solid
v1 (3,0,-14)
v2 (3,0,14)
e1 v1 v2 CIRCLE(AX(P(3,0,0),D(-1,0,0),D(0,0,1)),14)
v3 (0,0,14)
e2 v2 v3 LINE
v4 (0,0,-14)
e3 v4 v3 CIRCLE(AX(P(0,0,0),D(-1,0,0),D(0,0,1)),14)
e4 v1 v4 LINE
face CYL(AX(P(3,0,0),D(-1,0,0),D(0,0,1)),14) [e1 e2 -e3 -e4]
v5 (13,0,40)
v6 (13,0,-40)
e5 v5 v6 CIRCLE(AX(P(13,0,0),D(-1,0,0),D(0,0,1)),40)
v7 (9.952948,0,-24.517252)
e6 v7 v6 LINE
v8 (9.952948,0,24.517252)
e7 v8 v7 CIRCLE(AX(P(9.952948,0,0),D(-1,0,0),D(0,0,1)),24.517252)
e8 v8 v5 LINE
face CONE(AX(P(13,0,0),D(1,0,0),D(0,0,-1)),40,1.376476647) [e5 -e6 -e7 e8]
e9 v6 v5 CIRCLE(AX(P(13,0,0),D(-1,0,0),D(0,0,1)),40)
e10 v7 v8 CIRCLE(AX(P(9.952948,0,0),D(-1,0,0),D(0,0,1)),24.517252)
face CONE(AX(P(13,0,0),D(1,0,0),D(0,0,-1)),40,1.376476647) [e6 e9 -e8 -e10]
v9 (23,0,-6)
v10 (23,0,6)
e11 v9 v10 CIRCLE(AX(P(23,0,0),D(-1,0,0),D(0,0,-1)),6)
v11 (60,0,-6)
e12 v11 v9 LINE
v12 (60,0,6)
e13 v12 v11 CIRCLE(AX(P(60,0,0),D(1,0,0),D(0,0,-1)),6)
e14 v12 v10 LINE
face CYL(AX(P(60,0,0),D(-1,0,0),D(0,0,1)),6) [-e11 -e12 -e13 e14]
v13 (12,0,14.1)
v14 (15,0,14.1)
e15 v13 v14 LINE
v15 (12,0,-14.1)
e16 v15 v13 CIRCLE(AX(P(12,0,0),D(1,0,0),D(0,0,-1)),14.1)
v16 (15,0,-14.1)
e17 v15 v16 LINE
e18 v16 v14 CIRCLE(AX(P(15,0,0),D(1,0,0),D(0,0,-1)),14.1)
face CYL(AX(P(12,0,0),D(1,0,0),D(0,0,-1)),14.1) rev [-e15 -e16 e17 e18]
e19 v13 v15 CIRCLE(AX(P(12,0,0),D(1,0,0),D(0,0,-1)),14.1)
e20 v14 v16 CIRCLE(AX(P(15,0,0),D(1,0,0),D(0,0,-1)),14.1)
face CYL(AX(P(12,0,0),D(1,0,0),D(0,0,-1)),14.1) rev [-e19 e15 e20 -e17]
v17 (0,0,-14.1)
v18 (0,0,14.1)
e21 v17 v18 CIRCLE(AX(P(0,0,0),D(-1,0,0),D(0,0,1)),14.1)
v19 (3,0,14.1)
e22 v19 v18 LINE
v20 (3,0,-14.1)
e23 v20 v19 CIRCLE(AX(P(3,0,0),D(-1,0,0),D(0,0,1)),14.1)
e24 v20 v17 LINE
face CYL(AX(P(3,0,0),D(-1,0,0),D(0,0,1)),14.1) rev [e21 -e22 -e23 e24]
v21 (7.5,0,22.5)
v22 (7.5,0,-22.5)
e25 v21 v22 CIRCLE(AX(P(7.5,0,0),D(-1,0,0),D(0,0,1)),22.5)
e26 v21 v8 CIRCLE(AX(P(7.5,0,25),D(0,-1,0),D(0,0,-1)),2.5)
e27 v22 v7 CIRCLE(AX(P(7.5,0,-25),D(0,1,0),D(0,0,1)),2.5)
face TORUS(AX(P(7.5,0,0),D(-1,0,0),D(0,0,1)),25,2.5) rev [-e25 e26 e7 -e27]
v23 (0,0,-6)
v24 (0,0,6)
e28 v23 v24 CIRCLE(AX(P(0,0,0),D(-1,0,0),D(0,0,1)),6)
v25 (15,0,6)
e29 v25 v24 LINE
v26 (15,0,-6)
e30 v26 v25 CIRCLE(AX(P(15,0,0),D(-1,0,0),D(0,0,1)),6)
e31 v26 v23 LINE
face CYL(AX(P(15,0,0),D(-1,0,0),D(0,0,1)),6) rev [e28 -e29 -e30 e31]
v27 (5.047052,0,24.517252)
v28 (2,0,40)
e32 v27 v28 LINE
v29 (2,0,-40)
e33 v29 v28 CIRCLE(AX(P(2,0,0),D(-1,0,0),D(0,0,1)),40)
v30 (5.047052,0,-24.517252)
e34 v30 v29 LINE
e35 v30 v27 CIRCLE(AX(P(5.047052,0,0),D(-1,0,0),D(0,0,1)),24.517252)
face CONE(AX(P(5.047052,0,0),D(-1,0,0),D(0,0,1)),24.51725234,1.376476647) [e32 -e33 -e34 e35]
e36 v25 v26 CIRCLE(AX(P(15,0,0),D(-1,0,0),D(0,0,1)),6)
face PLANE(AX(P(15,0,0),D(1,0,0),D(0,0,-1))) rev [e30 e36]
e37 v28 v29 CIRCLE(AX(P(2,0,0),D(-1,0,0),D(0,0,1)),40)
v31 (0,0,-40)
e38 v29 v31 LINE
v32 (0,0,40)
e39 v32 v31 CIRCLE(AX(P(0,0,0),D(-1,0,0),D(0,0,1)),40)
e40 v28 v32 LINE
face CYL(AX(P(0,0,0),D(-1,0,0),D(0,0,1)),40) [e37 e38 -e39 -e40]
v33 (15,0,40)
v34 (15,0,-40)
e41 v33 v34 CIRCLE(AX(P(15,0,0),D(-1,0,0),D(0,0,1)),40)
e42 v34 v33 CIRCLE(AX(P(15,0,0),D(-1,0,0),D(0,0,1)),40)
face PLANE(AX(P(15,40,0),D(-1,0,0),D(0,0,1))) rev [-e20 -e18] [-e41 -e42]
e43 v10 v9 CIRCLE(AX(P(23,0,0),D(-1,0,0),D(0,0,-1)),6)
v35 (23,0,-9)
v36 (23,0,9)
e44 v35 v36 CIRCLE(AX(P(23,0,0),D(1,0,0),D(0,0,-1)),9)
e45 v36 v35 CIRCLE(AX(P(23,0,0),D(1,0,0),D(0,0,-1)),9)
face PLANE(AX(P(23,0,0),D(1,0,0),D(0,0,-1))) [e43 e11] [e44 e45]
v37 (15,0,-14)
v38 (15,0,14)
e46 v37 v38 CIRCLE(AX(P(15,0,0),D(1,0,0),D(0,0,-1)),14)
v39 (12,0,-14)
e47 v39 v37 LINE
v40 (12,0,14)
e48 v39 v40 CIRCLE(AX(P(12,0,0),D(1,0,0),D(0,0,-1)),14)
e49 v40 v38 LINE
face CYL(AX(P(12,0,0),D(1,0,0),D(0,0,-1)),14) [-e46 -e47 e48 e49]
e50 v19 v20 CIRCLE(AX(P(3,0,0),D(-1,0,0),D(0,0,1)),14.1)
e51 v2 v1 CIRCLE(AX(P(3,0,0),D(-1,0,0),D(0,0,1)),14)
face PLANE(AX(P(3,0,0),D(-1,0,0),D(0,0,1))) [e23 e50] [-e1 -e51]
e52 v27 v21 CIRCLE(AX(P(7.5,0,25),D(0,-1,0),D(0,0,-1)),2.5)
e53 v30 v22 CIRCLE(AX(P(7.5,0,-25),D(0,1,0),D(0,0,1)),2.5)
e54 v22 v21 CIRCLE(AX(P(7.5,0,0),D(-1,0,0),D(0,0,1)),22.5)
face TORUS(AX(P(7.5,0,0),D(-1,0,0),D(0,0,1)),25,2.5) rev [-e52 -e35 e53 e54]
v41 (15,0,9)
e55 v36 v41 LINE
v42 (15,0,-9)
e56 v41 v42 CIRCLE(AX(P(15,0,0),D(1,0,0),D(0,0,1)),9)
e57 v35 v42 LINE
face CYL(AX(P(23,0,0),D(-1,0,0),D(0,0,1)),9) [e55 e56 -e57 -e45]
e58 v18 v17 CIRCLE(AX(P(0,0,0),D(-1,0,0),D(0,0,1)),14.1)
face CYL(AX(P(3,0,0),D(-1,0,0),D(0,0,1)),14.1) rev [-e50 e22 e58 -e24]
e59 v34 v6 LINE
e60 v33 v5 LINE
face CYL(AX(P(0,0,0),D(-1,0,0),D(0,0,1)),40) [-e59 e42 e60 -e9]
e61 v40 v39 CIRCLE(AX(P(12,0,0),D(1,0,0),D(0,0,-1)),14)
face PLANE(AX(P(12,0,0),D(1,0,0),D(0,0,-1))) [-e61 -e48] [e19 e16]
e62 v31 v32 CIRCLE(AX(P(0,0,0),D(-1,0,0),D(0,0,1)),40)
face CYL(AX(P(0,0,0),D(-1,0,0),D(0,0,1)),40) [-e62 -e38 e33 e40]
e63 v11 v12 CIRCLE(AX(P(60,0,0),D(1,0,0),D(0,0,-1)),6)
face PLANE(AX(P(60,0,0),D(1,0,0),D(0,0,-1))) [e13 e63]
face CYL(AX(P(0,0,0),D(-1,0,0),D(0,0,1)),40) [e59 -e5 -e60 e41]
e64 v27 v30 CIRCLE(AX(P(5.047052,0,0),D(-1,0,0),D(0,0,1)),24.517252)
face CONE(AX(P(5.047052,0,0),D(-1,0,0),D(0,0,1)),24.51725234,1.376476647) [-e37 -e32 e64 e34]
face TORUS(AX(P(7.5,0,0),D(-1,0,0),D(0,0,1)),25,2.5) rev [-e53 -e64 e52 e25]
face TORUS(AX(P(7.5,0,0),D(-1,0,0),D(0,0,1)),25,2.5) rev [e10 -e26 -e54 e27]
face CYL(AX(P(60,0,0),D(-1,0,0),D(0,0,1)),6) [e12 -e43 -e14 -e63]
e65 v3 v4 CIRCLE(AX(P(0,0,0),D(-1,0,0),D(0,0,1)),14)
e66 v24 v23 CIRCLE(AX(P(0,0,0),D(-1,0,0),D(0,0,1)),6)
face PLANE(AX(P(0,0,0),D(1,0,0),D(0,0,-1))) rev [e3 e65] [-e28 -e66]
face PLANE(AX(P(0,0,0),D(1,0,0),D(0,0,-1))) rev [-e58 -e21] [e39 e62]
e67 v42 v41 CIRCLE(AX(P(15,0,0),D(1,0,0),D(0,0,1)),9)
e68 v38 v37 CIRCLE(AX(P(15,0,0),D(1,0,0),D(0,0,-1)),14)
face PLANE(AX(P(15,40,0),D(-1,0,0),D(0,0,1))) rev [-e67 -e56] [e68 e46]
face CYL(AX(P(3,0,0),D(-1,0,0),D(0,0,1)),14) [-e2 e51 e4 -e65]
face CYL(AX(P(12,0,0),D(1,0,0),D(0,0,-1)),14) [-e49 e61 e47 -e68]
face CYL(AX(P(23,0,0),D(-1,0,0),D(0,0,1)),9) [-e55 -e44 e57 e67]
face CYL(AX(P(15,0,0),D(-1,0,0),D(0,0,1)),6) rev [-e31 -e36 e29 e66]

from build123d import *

# Parameters (mm, degrees)
SKETCH2_R           = 6
CUT_EXTRUDE1_DEPTH  = 59.523499554
SKETCH3_R           = 14.1
SKETCH3_R_2         = 14
CUT_EXTRUDE2_DEPTH  = 3
CUT_EXTRUDE3_START  = -3
SKETCH4_R           = 14.1
SKETCH4_R_2         = 14
CUT_EXTRUDE3_DEPTH  = 3
SKETCH5_R           = 6
BOSS_EXTRUDE1_DEPTH = 45
SKETCH6_R           = 9
BOSS_EXTRUDE2_DEPTH = 8


with BuildPart() as part:
    # Sketch1 → Revolve1 (revolve)
    with BuildSketch(Plane.XY, mode=Mode.PRIVATE) as revolve1_sk:
        with BuildLine():
            Line((0, 0), (0, 40))
            Line((0, 40), (2, 40))
            Line((2, 40), (5.047051836, 24.51725234))
            ThreePointArc((5.047051836, 24.51725234), (7.5, 22.5), (9.952948164, 24.51725234))
            Line((9.952948164, 24.51725234), (13, 40))
            Line((13, 40), (15, 40))
            Line((15, 40), (15, 0))
            Line((15, 0), (0, 0))
        make_face()
    revolve(revolve1_sk.sketch.rotate(Axis((0, 0, 0), (1, 0, 0)), 90), axis=Axis((0, 0, 0), (1, 0, 0)))

    # Sketch2 → Cut-Extrude1 (cut, through all)
    with BuildSketch(Plane.ZY):
        Circle(SKETCH2_R)
    extrude(amount=-CUT_EXTRUDE1_DEPTH, mode=Mode.SUBTRACT)

    # Sketch3 → Cut-Extrude2 (cut)
    with BuildSketch(Plane.ZY):
        Circle(SKETCH3_R)
        Circle(SKETCH3_R_2, mode=Mode.SUBTRACT)
    extrude(amount=-CUT_EXTRUDE2_DEPTH, mode=Mode.SUBTRACT)

    # Sketch4 → Cut-Extrude3 (cut)
    with BuildSketch(Plane(origin=(15, 0, 0), x_dir=(0, 0, -1), z_dir=(1, 0, 0)).offset(CUT_EXTRUDE3_START)):
        with Locations(Location((0, 0, 0), (0, 0, 180))):
            Circle(SKETCH4_R)
        with Locations(Location((0, 0, 0), (0, 0, 180))):
            Circle(SKETCH4_R_2, mode=Mode.SUBTRACT)
    extrude(amount=CUT_EXTRUDE3_DEPTH, mode=Mode.SUBTRACT)



with BuildPart() as body_2:
    # Sketch5 → Boss-Extrude1 (new body)
    with BuildSketch(Plane(origin=(15, 0, 0), x_dir=(0, 0, -1), z_dir=(1, 0, 0))):
        with Locations(Location((0, 0, 0), (0, 0, 180))):
            Circle(SKETCH5_R)
    extrude(amount=BOSS_EXTRUDE1_DEPTH)


with BuildPart() as part_1:
    add(part.part)

    add(body_2.part)  # Boss-Extrude2 merges body 2
    # Sketch6 → Boss-Extrude2 (add)
    with BuildSketch(Plane(origin=(15, 0, 0), x_dir=(0, 0, -1), z_dir=(1, 0, 0))):
        with Locations(Location((0, 0, 0), (0, 0, 180))):
            Circle(SKETCH6_R)
    extrude(amount=BOSS_EXTRUDE2_DEPTH)


solid = part_1.part
